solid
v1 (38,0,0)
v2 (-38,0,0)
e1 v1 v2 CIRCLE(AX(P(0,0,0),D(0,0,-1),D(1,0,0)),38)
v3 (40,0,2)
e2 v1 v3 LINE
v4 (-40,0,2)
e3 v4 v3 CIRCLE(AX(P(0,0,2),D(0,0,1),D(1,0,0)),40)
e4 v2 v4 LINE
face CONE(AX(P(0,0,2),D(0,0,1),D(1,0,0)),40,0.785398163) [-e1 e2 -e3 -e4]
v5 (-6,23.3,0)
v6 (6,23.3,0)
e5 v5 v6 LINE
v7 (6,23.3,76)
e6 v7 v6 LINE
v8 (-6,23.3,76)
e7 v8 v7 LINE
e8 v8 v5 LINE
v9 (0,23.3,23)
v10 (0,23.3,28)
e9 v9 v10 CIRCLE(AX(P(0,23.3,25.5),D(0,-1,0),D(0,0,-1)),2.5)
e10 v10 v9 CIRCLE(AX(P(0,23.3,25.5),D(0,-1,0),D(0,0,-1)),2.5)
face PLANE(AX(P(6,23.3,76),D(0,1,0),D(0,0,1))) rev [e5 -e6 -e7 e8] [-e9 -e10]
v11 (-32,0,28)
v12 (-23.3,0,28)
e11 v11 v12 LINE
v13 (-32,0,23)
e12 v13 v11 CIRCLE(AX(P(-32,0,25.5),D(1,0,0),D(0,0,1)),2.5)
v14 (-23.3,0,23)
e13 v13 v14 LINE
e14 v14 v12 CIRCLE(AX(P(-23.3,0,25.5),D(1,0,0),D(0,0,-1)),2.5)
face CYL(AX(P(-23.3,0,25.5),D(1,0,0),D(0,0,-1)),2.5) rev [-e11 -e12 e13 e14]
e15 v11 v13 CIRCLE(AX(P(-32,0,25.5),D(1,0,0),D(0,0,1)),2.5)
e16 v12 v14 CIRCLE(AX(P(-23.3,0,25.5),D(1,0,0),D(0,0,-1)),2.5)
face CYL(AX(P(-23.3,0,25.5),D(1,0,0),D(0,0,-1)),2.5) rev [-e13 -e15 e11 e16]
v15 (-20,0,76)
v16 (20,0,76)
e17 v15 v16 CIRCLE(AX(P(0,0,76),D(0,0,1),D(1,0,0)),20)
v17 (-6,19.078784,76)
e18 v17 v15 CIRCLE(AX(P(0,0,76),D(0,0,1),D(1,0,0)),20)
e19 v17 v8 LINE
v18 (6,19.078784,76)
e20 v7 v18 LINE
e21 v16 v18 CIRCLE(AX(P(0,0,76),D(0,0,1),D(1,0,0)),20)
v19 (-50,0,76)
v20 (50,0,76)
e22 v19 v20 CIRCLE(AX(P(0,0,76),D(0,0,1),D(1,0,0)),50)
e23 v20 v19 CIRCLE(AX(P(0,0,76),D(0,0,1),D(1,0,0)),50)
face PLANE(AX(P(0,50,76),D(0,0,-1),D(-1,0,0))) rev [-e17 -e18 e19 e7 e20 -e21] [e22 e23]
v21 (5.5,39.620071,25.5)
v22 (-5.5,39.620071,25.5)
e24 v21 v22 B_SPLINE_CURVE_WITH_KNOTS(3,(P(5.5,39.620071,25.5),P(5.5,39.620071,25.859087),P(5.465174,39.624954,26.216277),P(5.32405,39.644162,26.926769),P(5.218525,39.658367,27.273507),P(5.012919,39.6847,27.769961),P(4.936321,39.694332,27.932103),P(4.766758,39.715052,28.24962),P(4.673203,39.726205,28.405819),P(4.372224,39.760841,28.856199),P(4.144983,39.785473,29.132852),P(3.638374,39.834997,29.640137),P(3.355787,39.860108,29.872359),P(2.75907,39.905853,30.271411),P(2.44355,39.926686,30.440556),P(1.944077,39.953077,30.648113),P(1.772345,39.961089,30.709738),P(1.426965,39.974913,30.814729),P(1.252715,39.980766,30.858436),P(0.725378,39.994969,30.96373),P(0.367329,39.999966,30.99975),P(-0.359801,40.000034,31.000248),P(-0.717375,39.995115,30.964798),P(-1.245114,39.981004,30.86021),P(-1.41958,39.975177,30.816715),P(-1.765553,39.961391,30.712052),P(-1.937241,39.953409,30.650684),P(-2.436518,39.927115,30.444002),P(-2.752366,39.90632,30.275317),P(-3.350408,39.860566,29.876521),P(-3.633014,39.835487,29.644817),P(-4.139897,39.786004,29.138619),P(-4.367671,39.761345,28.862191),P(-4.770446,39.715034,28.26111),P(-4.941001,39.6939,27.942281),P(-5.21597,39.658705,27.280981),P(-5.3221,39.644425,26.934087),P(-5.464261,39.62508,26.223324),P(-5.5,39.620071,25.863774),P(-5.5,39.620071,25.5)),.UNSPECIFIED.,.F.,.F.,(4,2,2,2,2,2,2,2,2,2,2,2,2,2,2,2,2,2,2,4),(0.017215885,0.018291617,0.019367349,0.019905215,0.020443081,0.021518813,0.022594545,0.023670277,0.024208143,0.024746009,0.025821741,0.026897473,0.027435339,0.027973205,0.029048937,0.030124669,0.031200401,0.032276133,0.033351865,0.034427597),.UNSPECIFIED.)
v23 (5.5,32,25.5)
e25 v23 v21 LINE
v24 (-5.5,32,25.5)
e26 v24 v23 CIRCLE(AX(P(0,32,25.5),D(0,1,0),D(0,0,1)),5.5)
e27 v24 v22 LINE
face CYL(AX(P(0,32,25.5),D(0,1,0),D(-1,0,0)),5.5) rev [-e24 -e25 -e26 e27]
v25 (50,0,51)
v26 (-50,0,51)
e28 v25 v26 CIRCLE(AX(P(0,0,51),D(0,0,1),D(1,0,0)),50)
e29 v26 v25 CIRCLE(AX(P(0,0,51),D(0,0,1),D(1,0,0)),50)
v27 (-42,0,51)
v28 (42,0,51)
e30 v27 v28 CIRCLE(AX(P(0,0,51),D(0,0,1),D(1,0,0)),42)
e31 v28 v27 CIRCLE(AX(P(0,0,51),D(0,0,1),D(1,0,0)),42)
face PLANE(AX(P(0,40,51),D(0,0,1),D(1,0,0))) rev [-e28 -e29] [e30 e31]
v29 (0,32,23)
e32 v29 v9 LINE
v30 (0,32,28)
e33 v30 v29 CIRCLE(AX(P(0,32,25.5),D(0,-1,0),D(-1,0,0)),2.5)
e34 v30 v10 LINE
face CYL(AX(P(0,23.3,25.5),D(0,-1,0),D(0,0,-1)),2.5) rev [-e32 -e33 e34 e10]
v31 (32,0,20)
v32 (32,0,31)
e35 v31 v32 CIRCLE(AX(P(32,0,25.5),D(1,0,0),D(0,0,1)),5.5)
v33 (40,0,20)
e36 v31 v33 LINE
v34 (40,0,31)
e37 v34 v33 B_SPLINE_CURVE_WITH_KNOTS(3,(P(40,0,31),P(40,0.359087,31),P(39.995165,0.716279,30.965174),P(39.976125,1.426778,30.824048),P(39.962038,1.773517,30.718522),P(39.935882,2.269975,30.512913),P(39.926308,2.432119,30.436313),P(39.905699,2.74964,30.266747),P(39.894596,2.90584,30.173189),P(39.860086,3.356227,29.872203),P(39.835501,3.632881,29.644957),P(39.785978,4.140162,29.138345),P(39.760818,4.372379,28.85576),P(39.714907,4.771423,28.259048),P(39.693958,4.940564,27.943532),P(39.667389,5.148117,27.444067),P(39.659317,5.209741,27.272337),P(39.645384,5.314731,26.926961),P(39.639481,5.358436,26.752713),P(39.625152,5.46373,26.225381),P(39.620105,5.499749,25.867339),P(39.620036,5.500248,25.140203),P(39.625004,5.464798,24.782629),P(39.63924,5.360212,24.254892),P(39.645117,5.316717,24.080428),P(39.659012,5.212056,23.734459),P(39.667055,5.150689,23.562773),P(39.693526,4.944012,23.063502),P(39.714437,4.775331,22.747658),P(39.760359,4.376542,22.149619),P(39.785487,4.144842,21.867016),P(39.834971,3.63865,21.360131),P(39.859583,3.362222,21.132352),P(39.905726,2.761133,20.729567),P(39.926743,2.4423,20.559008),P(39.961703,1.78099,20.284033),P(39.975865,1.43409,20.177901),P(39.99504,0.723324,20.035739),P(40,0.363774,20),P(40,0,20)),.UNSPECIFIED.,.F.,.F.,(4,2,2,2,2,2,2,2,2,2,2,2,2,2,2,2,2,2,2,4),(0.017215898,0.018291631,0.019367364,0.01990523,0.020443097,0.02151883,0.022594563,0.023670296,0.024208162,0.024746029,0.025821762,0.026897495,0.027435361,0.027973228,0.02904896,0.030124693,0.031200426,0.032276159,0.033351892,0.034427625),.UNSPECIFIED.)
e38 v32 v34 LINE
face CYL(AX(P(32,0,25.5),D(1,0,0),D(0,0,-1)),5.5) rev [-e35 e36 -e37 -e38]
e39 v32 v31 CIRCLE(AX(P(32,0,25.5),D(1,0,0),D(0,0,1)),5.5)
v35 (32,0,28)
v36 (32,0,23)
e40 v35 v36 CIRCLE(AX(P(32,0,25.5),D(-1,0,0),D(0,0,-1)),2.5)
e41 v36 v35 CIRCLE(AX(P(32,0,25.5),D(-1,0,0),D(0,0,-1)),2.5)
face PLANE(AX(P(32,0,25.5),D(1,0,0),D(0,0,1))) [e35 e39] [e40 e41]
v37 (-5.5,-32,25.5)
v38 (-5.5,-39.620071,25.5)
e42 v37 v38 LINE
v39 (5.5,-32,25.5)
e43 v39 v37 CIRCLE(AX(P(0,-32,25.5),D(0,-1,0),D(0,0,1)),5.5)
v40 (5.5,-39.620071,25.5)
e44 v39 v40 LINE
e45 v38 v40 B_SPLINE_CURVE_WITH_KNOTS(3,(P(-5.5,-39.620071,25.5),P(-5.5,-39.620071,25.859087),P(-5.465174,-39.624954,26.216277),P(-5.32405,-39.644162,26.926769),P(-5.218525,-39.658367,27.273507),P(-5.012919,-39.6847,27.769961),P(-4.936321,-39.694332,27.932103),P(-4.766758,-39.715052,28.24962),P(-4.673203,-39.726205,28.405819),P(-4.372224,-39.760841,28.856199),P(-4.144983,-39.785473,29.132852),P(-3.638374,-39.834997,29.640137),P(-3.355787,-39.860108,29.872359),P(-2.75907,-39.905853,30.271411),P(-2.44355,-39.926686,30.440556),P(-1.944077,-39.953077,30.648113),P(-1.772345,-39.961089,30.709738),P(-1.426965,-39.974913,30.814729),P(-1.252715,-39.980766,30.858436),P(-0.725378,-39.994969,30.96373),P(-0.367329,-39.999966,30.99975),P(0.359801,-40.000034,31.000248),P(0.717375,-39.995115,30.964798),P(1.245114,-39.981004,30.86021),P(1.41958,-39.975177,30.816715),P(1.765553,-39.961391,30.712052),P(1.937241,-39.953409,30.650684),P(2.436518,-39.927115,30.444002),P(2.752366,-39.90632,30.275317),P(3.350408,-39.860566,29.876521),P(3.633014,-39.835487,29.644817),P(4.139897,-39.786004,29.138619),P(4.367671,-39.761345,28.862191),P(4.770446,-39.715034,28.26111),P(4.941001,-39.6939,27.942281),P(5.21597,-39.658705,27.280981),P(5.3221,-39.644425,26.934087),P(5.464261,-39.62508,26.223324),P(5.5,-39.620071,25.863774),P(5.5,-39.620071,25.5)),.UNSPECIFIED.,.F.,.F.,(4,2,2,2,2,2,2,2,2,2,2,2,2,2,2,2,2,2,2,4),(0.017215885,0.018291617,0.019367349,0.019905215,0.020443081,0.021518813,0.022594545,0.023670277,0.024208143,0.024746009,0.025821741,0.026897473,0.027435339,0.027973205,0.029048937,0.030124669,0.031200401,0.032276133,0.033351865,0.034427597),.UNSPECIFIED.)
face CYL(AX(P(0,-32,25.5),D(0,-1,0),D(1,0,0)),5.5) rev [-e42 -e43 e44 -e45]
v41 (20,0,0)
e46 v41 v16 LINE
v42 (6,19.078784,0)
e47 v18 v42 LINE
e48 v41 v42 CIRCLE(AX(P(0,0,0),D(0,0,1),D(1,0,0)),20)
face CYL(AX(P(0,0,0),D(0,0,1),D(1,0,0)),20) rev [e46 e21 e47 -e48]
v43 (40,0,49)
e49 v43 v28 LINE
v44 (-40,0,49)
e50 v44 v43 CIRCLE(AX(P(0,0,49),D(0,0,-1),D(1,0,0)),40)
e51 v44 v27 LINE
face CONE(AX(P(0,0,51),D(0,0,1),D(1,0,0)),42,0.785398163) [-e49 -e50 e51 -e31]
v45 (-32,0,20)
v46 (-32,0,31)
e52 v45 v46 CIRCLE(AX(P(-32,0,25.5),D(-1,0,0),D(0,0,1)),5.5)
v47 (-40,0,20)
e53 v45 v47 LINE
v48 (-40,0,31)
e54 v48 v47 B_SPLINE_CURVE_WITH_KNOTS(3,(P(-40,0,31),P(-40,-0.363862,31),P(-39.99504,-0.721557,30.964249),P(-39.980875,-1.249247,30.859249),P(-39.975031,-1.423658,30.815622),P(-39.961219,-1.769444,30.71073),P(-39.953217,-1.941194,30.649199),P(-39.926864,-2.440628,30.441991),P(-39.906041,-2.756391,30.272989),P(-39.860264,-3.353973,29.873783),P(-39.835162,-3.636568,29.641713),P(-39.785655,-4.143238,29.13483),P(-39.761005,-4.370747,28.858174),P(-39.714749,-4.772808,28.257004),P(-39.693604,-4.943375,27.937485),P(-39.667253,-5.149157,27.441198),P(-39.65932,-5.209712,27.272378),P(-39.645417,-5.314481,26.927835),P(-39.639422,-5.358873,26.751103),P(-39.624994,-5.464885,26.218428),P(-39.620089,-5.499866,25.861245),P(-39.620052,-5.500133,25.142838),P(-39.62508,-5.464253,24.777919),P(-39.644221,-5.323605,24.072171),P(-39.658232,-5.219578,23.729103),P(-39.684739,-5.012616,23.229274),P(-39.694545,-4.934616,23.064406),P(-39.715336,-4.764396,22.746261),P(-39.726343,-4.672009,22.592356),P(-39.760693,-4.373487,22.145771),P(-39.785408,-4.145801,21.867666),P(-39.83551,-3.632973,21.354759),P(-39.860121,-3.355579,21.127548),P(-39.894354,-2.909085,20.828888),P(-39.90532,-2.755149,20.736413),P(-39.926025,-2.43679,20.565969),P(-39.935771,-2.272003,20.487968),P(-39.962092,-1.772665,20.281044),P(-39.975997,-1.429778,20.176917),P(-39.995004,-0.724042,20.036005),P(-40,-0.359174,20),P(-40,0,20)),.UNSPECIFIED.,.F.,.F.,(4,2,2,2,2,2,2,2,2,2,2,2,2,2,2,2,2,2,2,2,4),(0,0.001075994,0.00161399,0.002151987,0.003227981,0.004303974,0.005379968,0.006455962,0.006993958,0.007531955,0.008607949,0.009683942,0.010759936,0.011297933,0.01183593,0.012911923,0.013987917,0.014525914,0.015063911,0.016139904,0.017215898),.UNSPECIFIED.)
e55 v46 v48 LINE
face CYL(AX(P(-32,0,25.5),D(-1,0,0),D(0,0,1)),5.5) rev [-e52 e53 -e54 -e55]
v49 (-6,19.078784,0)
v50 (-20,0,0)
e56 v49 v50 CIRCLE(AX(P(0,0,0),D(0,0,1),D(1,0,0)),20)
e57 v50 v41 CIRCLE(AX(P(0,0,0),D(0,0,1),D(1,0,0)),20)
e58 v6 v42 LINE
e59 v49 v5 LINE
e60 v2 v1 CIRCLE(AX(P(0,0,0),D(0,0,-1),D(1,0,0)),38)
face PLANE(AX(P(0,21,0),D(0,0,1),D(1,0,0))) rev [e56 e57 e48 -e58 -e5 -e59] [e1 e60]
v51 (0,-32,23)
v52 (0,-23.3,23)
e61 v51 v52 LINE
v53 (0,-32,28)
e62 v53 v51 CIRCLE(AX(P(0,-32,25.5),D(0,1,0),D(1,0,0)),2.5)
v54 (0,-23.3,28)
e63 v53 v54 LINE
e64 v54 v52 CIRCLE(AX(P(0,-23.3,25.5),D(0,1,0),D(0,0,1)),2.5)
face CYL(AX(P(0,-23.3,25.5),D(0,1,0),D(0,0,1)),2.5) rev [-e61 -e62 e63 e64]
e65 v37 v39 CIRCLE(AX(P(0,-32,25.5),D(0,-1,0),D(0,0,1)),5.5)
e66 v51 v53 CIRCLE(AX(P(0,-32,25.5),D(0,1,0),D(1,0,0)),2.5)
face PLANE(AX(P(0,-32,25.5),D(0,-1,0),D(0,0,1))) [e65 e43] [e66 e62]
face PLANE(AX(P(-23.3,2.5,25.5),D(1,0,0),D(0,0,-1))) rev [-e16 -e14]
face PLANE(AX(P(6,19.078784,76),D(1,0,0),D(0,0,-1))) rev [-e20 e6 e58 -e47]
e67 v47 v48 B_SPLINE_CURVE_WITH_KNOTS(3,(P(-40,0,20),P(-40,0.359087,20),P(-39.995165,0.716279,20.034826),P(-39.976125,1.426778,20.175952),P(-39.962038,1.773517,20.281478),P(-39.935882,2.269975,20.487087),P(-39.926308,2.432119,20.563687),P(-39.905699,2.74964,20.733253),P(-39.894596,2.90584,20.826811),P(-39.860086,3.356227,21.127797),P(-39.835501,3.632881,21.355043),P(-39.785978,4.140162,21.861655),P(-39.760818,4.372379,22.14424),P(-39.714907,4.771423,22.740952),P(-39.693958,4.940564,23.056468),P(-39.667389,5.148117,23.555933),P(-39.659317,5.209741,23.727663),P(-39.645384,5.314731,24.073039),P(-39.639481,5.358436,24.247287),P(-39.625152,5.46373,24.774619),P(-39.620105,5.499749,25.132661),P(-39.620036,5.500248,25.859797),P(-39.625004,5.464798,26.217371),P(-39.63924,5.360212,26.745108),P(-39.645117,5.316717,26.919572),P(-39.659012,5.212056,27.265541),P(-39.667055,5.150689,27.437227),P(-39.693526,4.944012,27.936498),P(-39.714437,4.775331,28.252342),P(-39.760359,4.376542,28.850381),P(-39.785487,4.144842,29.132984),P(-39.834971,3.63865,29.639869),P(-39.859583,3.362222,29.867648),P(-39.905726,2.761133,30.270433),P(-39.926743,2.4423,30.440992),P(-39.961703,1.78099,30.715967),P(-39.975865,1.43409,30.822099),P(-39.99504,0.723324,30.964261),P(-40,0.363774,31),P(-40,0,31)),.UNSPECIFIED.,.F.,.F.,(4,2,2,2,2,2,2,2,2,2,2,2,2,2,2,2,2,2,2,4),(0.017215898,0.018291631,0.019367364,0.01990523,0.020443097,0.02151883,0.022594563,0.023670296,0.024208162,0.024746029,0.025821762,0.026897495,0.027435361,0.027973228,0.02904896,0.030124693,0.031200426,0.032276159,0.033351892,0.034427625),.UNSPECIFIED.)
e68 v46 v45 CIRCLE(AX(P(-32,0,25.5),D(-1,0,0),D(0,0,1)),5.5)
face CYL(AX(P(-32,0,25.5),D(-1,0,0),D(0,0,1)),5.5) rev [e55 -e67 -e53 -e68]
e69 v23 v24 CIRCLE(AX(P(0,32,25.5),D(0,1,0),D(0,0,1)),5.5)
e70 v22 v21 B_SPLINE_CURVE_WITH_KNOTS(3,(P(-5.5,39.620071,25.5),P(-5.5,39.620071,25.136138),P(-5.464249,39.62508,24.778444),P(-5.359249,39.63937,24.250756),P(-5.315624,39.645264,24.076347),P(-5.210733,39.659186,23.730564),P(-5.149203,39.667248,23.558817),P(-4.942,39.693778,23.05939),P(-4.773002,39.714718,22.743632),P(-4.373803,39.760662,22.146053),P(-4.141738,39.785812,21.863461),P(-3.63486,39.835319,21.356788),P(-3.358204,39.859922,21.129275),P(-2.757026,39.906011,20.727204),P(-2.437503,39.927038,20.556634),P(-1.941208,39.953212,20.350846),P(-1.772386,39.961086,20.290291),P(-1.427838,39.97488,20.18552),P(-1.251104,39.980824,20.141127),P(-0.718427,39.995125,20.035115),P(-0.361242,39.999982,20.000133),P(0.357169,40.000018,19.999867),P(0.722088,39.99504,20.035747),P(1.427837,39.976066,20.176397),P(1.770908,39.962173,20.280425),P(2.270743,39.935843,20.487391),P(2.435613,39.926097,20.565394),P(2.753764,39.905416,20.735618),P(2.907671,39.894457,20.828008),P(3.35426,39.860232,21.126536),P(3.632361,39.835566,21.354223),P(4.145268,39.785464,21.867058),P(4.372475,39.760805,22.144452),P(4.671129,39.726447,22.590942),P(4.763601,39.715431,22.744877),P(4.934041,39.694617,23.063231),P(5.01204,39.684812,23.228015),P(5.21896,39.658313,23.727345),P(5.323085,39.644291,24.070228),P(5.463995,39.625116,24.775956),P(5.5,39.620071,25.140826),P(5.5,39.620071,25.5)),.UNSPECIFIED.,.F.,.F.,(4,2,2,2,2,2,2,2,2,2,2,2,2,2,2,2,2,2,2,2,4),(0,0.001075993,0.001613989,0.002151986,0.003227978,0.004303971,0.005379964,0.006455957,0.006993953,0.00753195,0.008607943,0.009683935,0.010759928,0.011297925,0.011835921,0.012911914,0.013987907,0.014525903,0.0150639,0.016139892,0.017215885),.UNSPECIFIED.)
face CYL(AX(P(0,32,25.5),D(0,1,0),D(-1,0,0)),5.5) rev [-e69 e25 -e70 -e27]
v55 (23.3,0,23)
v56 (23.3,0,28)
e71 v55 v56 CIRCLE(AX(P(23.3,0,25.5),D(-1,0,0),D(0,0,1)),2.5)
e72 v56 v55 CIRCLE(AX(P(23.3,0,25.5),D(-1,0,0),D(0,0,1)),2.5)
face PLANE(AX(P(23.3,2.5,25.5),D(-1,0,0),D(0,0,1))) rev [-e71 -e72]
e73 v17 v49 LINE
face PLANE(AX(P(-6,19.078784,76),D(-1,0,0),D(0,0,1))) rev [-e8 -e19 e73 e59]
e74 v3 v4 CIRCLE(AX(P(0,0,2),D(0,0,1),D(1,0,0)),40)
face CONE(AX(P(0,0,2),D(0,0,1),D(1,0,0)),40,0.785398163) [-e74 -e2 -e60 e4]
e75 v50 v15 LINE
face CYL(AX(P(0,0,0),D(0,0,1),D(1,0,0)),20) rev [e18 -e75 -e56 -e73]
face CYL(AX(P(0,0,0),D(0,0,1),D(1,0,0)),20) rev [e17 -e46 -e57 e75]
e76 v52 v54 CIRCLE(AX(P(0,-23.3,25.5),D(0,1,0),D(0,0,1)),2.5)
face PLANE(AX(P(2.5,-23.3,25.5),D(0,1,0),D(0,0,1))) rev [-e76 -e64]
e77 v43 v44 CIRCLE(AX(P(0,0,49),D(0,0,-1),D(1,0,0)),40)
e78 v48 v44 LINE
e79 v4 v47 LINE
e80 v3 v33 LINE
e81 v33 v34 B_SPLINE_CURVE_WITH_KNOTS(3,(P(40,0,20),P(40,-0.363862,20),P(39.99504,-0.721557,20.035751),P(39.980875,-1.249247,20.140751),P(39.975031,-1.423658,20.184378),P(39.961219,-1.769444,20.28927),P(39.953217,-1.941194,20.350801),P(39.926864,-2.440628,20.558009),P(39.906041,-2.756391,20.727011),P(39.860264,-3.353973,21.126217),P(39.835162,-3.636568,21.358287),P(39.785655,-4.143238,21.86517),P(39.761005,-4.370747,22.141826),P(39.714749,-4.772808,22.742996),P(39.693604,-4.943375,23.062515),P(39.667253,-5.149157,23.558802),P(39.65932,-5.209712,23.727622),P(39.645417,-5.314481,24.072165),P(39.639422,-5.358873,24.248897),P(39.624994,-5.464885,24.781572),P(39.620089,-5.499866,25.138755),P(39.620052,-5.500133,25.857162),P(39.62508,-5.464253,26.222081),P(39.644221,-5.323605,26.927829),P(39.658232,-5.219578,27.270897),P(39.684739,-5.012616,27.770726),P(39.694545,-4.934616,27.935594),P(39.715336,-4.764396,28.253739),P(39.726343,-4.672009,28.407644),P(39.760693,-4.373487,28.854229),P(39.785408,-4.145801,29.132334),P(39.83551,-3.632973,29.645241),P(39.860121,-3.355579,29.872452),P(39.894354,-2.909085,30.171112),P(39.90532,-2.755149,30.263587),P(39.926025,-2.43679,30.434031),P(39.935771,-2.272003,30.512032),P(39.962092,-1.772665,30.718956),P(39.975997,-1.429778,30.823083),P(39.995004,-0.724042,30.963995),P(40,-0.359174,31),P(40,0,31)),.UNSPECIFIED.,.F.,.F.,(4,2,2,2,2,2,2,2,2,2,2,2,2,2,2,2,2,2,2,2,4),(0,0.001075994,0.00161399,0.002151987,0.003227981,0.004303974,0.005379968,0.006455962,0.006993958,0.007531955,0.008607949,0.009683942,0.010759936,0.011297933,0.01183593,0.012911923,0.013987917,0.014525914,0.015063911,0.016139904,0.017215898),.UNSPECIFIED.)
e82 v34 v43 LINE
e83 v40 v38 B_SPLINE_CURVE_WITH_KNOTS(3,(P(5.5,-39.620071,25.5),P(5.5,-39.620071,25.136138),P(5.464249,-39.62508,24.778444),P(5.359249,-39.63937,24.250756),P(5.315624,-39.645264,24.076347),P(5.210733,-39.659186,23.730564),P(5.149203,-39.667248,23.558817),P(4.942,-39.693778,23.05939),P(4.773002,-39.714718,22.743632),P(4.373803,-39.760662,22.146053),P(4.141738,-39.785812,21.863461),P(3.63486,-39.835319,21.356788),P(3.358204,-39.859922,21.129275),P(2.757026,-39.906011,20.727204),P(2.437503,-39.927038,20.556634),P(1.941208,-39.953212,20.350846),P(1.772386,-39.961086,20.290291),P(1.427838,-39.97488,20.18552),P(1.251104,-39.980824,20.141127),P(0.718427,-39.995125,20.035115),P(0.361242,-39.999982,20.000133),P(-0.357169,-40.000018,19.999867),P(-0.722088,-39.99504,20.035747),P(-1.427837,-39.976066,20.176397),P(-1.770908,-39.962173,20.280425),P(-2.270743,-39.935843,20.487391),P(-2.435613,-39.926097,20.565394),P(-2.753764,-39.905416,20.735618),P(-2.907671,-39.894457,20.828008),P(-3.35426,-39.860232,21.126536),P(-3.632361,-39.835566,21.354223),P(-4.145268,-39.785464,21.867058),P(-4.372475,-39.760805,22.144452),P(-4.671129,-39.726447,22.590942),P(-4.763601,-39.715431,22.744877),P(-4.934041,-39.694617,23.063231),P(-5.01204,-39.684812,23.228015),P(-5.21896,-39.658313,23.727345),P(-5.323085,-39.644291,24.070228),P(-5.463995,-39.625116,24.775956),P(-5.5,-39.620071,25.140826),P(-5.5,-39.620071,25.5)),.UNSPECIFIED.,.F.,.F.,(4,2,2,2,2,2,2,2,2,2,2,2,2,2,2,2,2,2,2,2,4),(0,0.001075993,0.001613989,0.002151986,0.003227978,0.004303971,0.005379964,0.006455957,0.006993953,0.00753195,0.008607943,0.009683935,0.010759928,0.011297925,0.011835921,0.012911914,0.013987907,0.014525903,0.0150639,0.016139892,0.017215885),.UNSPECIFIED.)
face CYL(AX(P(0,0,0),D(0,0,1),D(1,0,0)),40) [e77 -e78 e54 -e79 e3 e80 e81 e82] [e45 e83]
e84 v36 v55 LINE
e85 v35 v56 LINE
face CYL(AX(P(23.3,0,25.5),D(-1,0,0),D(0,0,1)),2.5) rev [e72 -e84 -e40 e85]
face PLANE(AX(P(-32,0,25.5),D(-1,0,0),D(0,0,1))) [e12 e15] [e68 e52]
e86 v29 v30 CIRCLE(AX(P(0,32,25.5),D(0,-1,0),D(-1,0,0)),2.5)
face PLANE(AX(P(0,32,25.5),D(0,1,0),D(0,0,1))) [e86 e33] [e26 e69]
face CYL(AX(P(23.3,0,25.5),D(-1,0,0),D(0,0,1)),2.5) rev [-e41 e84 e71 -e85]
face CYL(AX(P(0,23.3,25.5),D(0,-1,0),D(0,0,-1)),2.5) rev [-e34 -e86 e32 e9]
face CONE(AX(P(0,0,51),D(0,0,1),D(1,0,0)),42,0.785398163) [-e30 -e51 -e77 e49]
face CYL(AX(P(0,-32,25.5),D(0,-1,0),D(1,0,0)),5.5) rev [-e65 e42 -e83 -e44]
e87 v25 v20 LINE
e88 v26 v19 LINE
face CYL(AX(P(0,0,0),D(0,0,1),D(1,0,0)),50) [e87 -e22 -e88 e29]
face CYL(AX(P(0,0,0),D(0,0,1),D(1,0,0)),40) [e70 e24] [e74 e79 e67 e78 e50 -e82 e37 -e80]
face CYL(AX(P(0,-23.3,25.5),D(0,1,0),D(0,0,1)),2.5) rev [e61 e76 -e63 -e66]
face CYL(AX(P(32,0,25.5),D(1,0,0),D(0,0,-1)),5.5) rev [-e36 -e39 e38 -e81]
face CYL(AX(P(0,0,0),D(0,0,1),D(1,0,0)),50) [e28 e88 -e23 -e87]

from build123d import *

# Parameters (mm, degrees)
CHAMFER_1_SIZE           = 2
CHAMFER_2_SIZE           = 2
SKETCH_8_R               = 30
SKETCH_8_R_2             = 20
EXTRUDE_1_DEPTH          = 76
SKETCH_9_W               = 12
SKETCH_9_H               = 4.221215972
CUT_EXTRUDE_1_DEPTH      = 104.807514179
SKETCH_11_W              = 2.5
SKETCH_11_H              = 26.7
PATTERN_CIRCULAR_2_COUNT = 4
SKETCH_14_R              = 5.5
CUT_EXTRUDE_2_DEPTH      = 8
PATTERN_CIRCULAR_3_COUNT = 4


with BuildPart() as part:
    # 草图1 → 旋转1 (revolve)
    with BuildSketch(Plane(origin=(0, 0, 0), x_dir=(0, 0, -1), z_dir=(1, 0, 0)), mode=Mode.PRIVATE) as revolve_1_sk:
        Polygon((0, 21), (0, 40), (-51, 40), (-51, 50), (-76, 50), (-76, 30), (-16, 30), (-16, 21), align=None)
    revolve(revolve_1_sk.sketch.rotate(Axis((0, 0, 0), (0, 0, -1)), 90), axis=Axis((0, 0, 0), (0, 0, -1)))

    # 倒角1
    chamfer_1_edges = [part.edges().sort_by_distance(p)[0] for p in [
        (-40, 0, 51),
    ]]
    chamfer(chamfer_1_edges, length=CHAMFER_1_SIZE)

    # 倒角2
    chamfer_2_edges = [part.edges().sort_by_distance(p)[0] for p in [
        (-40, 0, 0),
    ]]
    chamfer(chamfer_2_edges, length=CHAMFER_2_SIZE)

    # 草图8 → 凸台-拉伸1 (add, through all)
    with BuildSketch(Plane.XY.offset(76)):
        Circle(SKETCH_8_R)
        Circle(SKETCH_8_R_2, mode=Mode.SUBTRACT)
    extrude(amount=-EXTRUDE_1_DEPTH)

    # 草图9 → 切除-拉伸1 (cut, through all)
    with BuildSketch(Plane(origin=(0, 0, 0), x_dir=(-1, 0, 0), z_dir=(0, 0, -1))):
        with Locations((0, 21.189392014)):
            Rectangle(SKETCH_9_W, SKETCH_9_H)
    extrude(amount=-CUT_EXTRUDE_1_DEPTH, mode=Mode.SUBTRACT)

    # 草图11 → M6 螺纹孔1 (revolve, cut)
    with BuildSketch(Plane(origin=(0, 23.3, 25.5), x_dir=(0, 0, -1), z_dir=(1, 0, 0))):
        with Locations((1.25, 13.35)):
            Rectangle(SKETCH_11_W, SKETCH_11_H)
    hole_wizard_m6_1 = revolve(axis=Axis((0, 16.95, 25.5), (0, 1, 0)), mode=Mode.SUBTRACT)

    # 阵列(圆周)2: M6 螺纹孔1 ×4 about axis
    pattern_circular_2_axis = Axis((0, 0, 0), (0, 0, 1))
    for i in range(1, PATTERN_CIRCULAR_2_COUNT):
        add(hole_wizard_m6_1.rotate(pattern_circular_2_axis, i * 360 / PATTERN_CIRCULAR_2_COUNT), mode=Mode.SUBTRACT)

    # 草图14 → 切除-拉伸2 (cut)
    with BuildSketch(Plane.ZY.offset(40)):
        with Locations((25.5, 0)):
            Circle(SKETCH_14_R)
    cut_extrude_2 = extrude(amount=-CUT_EXTRUDE_2_DEPTH, mode=Mode.SUBTRACT)

    # 阵列(圆周)3: 切除-拉伸2 ×4 about axis
    pattern_circular_3_axis = Axis((0, 0, 0), (0, 0, 1))
    for i in range(1, PATTERN_CIRCULAR_3_COUNT):
        add(cut_extrude_2.rotate(pattern_circular_3_axis, i * 360 / PATTERN_CIRCULAR_3_COUNT), mode=Mode.SUBTRACT)


solid = part.part
